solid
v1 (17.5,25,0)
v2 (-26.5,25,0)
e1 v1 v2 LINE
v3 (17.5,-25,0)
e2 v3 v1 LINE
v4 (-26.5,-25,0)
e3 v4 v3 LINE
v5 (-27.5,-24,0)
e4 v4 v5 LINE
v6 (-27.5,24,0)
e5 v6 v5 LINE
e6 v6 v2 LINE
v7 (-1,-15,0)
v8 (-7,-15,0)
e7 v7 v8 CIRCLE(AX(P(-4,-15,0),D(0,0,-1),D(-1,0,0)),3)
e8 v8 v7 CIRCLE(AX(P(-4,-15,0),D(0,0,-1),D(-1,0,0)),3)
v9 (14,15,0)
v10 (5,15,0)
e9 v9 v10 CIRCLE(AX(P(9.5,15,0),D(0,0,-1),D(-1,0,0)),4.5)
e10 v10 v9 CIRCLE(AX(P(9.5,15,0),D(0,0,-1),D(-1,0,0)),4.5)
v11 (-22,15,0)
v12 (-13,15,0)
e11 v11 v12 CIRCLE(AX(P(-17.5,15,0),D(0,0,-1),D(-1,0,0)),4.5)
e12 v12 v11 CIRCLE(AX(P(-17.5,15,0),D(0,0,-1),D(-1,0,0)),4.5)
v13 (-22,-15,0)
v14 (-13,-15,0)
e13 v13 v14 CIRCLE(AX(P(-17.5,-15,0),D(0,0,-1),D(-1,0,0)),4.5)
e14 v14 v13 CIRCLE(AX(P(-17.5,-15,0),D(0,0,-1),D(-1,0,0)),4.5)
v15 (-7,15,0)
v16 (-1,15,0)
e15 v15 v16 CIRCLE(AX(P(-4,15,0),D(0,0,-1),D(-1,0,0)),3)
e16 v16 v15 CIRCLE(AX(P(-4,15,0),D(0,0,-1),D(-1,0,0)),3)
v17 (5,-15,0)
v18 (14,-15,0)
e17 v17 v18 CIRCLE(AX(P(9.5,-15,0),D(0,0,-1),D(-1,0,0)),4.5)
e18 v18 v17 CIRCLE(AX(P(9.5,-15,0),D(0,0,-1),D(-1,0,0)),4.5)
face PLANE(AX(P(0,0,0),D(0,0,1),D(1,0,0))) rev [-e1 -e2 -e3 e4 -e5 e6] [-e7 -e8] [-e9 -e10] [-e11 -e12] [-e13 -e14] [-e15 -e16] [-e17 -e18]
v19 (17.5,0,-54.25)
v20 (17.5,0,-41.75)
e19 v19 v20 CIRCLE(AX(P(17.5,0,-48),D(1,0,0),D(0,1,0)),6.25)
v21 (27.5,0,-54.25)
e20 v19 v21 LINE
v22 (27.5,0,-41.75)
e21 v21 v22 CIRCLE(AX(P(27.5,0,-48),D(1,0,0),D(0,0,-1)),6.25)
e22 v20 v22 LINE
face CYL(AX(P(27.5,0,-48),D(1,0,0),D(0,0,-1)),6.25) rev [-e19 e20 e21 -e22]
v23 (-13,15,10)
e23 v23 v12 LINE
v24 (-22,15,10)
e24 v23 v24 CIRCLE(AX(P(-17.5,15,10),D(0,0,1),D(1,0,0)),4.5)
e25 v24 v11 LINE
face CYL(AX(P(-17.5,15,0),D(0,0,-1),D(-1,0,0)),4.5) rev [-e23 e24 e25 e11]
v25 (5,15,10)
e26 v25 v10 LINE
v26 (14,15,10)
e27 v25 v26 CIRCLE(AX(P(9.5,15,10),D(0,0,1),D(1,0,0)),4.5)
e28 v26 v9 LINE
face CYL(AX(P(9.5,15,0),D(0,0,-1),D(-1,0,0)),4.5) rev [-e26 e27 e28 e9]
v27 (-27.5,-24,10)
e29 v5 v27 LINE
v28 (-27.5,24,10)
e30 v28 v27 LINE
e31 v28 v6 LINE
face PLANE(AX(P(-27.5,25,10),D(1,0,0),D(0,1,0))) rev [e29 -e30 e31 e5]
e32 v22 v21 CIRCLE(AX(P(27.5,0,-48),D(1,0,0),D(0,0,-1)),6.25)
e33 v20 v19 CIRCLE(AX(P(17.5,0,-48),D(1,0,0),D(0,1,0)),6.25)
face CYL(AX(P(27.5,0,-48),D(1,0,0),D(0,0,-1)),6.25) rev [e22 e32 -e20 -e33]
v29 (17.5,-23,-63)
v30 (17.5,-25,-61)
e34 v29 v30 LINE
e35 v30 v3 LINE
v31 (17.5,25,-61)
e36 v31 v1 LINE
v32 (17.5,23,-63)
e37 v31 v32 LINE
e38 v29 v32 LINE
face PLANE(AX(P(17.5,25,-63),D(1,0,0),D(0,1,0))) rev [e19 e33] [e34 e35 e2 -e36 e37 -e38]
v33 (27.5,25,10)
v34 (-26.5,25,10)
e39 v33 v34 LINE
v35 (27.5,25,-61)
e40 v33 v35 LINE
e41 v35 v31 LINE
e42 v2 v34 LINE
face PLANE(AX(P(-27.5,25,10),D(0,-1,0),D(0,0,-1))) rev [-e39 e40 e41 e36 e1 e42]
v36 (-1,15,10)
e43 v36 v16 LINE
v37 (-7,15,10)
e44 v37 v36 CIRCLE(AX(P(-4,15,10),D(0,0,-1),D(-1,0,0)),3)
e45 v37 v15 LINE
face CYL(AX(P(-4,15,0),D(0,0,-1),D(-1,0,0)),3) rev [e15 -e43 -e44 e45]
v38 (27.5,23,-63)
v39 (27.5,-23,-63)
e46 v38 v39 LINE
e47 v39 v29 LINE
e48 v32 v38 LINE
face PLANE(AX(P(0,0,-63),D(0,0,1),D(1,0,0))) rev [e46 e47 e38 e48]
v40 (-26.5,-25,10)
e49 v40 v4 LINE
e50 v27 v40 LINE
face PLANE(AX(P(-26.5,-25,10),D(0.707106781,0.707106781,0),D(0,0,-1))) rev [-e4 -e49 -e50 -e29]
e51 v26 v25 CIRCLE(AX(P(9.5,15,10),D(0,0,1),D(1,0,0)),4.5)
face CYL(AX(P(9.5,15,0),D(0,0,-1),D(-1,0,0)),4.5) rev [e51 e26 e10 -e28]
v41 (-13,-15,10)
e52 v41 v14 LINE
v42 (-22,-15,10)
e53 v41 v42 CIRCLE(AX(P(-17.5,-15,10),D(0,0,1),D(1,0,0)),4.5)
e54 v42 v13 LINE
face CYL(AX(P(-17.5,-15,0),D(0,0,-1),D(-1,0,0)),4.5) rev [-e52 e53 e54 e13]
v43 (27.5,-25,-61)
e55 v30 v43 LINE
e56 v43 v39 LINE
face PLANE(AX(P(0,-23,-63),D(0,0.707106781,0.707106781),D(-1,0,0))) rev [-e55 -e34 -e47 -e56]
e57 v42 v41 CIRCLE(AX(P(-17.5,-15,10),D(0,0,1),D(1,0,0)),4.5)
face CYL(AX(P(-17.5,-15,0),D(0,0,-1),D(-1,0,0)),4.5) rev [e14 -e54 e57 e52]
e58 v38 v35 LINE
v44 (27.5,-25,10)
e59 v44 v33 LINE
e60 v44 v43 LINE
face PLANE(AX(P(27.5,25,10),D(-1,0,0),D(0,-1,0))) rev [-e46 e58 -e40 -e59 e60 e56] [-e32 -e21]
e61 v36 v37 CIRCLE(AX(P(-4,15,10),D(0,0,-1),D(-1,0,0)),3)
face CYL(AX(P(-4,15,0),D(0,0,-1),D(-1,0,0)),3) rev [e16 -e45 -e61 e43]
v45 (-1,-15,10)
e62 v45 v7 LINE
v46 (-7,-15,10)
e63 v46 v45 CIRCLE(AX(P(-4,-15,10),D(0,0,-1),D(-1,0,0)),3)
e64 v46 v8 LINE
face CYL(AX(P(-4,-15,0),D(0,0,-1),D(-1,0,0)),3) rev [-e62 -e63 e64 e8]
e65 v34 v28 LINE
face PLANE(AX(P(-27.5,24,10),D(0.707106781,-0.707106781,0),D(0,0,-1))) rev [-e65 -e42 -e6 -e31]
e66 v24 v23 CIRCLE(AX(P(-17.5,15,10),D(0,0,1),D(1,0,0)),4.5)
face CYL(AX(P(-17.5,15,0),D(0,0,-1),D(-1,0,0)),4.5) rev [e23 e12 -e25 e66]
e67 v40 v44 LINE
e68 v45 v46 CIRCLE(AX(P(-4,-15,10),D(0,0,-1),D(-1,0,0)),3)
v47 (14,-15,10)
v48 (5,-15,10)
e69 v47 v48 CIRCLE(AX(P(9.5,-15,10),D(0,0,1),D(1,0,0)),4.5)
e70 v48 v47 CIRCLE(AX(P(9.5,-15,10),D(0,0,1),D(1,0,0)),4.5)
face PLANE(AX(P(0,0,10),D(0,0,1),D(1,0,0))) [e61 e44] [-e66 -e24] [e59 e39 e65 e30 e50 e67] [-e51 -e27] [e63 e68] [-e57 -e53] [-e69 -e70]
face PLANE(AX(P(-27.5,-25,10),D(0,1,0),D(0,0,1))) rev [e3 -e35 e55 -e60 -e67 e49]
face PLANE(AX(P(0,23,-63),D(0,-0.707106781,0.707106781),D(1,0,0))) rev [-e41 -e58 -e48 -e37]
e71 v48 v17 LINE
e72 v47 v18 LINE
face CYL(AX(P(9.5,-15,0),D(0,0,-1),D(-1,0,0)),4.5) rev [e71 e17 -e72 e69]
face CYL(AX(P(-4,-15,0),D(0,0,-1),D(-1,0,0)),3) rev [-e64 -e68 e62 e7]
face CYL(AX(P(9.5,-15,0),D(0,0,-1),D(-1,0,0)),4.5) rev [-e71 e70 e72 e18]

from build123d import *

# Parameters (mm, degrees)
SKETCH1_W                    = 55
SKETCH1_H                    = 50
BOSS_EXTRUDE1_DEPTH          = 10
SKETCH4_W                    = 10
SKETCH4_H                    = 50
BOSS_EXTRUDE2_DEPTH          = 63
M8_CLEARANCE_HOLE1_D         = 9
M8_CLEARANCE_HOLE1_DEPTH     = 121
M8_CLEARANCE_HOLE1_TIP       = 2.703872786
CHAMFER1_SIZE                = 1
M14X1_5_TAPPED_HOLE1_D       = 12.5
CHAMFER2_SIZE                = 2
SIZE_MM_BLIND_DOWEL_HOLE_1_D = 6


with BuildPart() as part:
    # Sketch1 → Boss-Extrude1 (new body)
    with BuildSketch(Plane.XY):
        Rectangle(SKETCH1_W, SKETCH1_H)
    extrude(amount=BOSS_EXTRUDE1_DEPTH)

    # Sketch4 → Boss-Extrude2 (add)
    with BuildSketch(Plane(origin=(0, 0, 0), x_dir=(-1, 0, 0), z_dir=(0, 0, -1))):
        with Locations((-22.5, 0)):
            Rectangle(SKETCH4_W, SKETCH4_H)
    extrude(amount=BOSS_EXTRUDE2_DEPTH)

    # M8 Clearance Hole1
    with Locations(Plane(origin=(0, 0, 0), x_dir=(-1, 0, 0), z_dir=(0, 0, -1))):
        with Locations((17.5, -15), (17.5, 15), (-9.5, -15), (-9.5, 15)):
            Hole(M8_CLEARANCE_HOLE1_D / 2, depth=M8_CLEARANCE_HOLE1_DEPTH)
            with Locations((0, 0, -(M8_CLEARANCE_HOLE1_DEPTH + M8_CLEARANCE_HOLE1_TIP / 2))):  # 118° drill point
                Cone(0, M8_CLEARANCE_HOLE1_D / 2, M8_CLEARANCE_HOLE1_TIP, mode=Mode.SUBTRACT)

    # Chamfer1
    chamfer1_edges = [part.edges().sort_by_distance(p)[0] for p in [
        (-27.5, -25, 5),
        (-27.5, 25, 5),
    ]]
    chamfer(chamfer1_edges, length=CHAMFER1_SIZE)

    # M14x1.5 Tapped Hole1 (through all)
    with Locations(Plane(origin=(27.5, 0, 0), x_dir=(0, 0, -1), z_dir=(1, 0, 0))):
        with Locations((48, 0)):
            Hole(M14X1_5_TAPPED_HOLE1_D / 2)

    # Chamfer2
    chamfer2_edges = [part.edges().sort_by_distance(p)[0] for p in [
        (22.5, 25, -63),
        (22.5, -25, -63),
    ]]
    chamfer(chamfer2_edges, length=CHAMFER2_SIZE)

    # Size mm blind dowel hole 1 (through all)
    with Locations(Plane(origin=(0, 0, 0), x_dir=(-1, 0, 0), z_dir=(0, 0, -1))):
        with Locations((4, -15), (4, 15)):
            Hole(SIZE_MM_BLIND_DOWEL_HOLE_1_D / 2)


solid = part.part
